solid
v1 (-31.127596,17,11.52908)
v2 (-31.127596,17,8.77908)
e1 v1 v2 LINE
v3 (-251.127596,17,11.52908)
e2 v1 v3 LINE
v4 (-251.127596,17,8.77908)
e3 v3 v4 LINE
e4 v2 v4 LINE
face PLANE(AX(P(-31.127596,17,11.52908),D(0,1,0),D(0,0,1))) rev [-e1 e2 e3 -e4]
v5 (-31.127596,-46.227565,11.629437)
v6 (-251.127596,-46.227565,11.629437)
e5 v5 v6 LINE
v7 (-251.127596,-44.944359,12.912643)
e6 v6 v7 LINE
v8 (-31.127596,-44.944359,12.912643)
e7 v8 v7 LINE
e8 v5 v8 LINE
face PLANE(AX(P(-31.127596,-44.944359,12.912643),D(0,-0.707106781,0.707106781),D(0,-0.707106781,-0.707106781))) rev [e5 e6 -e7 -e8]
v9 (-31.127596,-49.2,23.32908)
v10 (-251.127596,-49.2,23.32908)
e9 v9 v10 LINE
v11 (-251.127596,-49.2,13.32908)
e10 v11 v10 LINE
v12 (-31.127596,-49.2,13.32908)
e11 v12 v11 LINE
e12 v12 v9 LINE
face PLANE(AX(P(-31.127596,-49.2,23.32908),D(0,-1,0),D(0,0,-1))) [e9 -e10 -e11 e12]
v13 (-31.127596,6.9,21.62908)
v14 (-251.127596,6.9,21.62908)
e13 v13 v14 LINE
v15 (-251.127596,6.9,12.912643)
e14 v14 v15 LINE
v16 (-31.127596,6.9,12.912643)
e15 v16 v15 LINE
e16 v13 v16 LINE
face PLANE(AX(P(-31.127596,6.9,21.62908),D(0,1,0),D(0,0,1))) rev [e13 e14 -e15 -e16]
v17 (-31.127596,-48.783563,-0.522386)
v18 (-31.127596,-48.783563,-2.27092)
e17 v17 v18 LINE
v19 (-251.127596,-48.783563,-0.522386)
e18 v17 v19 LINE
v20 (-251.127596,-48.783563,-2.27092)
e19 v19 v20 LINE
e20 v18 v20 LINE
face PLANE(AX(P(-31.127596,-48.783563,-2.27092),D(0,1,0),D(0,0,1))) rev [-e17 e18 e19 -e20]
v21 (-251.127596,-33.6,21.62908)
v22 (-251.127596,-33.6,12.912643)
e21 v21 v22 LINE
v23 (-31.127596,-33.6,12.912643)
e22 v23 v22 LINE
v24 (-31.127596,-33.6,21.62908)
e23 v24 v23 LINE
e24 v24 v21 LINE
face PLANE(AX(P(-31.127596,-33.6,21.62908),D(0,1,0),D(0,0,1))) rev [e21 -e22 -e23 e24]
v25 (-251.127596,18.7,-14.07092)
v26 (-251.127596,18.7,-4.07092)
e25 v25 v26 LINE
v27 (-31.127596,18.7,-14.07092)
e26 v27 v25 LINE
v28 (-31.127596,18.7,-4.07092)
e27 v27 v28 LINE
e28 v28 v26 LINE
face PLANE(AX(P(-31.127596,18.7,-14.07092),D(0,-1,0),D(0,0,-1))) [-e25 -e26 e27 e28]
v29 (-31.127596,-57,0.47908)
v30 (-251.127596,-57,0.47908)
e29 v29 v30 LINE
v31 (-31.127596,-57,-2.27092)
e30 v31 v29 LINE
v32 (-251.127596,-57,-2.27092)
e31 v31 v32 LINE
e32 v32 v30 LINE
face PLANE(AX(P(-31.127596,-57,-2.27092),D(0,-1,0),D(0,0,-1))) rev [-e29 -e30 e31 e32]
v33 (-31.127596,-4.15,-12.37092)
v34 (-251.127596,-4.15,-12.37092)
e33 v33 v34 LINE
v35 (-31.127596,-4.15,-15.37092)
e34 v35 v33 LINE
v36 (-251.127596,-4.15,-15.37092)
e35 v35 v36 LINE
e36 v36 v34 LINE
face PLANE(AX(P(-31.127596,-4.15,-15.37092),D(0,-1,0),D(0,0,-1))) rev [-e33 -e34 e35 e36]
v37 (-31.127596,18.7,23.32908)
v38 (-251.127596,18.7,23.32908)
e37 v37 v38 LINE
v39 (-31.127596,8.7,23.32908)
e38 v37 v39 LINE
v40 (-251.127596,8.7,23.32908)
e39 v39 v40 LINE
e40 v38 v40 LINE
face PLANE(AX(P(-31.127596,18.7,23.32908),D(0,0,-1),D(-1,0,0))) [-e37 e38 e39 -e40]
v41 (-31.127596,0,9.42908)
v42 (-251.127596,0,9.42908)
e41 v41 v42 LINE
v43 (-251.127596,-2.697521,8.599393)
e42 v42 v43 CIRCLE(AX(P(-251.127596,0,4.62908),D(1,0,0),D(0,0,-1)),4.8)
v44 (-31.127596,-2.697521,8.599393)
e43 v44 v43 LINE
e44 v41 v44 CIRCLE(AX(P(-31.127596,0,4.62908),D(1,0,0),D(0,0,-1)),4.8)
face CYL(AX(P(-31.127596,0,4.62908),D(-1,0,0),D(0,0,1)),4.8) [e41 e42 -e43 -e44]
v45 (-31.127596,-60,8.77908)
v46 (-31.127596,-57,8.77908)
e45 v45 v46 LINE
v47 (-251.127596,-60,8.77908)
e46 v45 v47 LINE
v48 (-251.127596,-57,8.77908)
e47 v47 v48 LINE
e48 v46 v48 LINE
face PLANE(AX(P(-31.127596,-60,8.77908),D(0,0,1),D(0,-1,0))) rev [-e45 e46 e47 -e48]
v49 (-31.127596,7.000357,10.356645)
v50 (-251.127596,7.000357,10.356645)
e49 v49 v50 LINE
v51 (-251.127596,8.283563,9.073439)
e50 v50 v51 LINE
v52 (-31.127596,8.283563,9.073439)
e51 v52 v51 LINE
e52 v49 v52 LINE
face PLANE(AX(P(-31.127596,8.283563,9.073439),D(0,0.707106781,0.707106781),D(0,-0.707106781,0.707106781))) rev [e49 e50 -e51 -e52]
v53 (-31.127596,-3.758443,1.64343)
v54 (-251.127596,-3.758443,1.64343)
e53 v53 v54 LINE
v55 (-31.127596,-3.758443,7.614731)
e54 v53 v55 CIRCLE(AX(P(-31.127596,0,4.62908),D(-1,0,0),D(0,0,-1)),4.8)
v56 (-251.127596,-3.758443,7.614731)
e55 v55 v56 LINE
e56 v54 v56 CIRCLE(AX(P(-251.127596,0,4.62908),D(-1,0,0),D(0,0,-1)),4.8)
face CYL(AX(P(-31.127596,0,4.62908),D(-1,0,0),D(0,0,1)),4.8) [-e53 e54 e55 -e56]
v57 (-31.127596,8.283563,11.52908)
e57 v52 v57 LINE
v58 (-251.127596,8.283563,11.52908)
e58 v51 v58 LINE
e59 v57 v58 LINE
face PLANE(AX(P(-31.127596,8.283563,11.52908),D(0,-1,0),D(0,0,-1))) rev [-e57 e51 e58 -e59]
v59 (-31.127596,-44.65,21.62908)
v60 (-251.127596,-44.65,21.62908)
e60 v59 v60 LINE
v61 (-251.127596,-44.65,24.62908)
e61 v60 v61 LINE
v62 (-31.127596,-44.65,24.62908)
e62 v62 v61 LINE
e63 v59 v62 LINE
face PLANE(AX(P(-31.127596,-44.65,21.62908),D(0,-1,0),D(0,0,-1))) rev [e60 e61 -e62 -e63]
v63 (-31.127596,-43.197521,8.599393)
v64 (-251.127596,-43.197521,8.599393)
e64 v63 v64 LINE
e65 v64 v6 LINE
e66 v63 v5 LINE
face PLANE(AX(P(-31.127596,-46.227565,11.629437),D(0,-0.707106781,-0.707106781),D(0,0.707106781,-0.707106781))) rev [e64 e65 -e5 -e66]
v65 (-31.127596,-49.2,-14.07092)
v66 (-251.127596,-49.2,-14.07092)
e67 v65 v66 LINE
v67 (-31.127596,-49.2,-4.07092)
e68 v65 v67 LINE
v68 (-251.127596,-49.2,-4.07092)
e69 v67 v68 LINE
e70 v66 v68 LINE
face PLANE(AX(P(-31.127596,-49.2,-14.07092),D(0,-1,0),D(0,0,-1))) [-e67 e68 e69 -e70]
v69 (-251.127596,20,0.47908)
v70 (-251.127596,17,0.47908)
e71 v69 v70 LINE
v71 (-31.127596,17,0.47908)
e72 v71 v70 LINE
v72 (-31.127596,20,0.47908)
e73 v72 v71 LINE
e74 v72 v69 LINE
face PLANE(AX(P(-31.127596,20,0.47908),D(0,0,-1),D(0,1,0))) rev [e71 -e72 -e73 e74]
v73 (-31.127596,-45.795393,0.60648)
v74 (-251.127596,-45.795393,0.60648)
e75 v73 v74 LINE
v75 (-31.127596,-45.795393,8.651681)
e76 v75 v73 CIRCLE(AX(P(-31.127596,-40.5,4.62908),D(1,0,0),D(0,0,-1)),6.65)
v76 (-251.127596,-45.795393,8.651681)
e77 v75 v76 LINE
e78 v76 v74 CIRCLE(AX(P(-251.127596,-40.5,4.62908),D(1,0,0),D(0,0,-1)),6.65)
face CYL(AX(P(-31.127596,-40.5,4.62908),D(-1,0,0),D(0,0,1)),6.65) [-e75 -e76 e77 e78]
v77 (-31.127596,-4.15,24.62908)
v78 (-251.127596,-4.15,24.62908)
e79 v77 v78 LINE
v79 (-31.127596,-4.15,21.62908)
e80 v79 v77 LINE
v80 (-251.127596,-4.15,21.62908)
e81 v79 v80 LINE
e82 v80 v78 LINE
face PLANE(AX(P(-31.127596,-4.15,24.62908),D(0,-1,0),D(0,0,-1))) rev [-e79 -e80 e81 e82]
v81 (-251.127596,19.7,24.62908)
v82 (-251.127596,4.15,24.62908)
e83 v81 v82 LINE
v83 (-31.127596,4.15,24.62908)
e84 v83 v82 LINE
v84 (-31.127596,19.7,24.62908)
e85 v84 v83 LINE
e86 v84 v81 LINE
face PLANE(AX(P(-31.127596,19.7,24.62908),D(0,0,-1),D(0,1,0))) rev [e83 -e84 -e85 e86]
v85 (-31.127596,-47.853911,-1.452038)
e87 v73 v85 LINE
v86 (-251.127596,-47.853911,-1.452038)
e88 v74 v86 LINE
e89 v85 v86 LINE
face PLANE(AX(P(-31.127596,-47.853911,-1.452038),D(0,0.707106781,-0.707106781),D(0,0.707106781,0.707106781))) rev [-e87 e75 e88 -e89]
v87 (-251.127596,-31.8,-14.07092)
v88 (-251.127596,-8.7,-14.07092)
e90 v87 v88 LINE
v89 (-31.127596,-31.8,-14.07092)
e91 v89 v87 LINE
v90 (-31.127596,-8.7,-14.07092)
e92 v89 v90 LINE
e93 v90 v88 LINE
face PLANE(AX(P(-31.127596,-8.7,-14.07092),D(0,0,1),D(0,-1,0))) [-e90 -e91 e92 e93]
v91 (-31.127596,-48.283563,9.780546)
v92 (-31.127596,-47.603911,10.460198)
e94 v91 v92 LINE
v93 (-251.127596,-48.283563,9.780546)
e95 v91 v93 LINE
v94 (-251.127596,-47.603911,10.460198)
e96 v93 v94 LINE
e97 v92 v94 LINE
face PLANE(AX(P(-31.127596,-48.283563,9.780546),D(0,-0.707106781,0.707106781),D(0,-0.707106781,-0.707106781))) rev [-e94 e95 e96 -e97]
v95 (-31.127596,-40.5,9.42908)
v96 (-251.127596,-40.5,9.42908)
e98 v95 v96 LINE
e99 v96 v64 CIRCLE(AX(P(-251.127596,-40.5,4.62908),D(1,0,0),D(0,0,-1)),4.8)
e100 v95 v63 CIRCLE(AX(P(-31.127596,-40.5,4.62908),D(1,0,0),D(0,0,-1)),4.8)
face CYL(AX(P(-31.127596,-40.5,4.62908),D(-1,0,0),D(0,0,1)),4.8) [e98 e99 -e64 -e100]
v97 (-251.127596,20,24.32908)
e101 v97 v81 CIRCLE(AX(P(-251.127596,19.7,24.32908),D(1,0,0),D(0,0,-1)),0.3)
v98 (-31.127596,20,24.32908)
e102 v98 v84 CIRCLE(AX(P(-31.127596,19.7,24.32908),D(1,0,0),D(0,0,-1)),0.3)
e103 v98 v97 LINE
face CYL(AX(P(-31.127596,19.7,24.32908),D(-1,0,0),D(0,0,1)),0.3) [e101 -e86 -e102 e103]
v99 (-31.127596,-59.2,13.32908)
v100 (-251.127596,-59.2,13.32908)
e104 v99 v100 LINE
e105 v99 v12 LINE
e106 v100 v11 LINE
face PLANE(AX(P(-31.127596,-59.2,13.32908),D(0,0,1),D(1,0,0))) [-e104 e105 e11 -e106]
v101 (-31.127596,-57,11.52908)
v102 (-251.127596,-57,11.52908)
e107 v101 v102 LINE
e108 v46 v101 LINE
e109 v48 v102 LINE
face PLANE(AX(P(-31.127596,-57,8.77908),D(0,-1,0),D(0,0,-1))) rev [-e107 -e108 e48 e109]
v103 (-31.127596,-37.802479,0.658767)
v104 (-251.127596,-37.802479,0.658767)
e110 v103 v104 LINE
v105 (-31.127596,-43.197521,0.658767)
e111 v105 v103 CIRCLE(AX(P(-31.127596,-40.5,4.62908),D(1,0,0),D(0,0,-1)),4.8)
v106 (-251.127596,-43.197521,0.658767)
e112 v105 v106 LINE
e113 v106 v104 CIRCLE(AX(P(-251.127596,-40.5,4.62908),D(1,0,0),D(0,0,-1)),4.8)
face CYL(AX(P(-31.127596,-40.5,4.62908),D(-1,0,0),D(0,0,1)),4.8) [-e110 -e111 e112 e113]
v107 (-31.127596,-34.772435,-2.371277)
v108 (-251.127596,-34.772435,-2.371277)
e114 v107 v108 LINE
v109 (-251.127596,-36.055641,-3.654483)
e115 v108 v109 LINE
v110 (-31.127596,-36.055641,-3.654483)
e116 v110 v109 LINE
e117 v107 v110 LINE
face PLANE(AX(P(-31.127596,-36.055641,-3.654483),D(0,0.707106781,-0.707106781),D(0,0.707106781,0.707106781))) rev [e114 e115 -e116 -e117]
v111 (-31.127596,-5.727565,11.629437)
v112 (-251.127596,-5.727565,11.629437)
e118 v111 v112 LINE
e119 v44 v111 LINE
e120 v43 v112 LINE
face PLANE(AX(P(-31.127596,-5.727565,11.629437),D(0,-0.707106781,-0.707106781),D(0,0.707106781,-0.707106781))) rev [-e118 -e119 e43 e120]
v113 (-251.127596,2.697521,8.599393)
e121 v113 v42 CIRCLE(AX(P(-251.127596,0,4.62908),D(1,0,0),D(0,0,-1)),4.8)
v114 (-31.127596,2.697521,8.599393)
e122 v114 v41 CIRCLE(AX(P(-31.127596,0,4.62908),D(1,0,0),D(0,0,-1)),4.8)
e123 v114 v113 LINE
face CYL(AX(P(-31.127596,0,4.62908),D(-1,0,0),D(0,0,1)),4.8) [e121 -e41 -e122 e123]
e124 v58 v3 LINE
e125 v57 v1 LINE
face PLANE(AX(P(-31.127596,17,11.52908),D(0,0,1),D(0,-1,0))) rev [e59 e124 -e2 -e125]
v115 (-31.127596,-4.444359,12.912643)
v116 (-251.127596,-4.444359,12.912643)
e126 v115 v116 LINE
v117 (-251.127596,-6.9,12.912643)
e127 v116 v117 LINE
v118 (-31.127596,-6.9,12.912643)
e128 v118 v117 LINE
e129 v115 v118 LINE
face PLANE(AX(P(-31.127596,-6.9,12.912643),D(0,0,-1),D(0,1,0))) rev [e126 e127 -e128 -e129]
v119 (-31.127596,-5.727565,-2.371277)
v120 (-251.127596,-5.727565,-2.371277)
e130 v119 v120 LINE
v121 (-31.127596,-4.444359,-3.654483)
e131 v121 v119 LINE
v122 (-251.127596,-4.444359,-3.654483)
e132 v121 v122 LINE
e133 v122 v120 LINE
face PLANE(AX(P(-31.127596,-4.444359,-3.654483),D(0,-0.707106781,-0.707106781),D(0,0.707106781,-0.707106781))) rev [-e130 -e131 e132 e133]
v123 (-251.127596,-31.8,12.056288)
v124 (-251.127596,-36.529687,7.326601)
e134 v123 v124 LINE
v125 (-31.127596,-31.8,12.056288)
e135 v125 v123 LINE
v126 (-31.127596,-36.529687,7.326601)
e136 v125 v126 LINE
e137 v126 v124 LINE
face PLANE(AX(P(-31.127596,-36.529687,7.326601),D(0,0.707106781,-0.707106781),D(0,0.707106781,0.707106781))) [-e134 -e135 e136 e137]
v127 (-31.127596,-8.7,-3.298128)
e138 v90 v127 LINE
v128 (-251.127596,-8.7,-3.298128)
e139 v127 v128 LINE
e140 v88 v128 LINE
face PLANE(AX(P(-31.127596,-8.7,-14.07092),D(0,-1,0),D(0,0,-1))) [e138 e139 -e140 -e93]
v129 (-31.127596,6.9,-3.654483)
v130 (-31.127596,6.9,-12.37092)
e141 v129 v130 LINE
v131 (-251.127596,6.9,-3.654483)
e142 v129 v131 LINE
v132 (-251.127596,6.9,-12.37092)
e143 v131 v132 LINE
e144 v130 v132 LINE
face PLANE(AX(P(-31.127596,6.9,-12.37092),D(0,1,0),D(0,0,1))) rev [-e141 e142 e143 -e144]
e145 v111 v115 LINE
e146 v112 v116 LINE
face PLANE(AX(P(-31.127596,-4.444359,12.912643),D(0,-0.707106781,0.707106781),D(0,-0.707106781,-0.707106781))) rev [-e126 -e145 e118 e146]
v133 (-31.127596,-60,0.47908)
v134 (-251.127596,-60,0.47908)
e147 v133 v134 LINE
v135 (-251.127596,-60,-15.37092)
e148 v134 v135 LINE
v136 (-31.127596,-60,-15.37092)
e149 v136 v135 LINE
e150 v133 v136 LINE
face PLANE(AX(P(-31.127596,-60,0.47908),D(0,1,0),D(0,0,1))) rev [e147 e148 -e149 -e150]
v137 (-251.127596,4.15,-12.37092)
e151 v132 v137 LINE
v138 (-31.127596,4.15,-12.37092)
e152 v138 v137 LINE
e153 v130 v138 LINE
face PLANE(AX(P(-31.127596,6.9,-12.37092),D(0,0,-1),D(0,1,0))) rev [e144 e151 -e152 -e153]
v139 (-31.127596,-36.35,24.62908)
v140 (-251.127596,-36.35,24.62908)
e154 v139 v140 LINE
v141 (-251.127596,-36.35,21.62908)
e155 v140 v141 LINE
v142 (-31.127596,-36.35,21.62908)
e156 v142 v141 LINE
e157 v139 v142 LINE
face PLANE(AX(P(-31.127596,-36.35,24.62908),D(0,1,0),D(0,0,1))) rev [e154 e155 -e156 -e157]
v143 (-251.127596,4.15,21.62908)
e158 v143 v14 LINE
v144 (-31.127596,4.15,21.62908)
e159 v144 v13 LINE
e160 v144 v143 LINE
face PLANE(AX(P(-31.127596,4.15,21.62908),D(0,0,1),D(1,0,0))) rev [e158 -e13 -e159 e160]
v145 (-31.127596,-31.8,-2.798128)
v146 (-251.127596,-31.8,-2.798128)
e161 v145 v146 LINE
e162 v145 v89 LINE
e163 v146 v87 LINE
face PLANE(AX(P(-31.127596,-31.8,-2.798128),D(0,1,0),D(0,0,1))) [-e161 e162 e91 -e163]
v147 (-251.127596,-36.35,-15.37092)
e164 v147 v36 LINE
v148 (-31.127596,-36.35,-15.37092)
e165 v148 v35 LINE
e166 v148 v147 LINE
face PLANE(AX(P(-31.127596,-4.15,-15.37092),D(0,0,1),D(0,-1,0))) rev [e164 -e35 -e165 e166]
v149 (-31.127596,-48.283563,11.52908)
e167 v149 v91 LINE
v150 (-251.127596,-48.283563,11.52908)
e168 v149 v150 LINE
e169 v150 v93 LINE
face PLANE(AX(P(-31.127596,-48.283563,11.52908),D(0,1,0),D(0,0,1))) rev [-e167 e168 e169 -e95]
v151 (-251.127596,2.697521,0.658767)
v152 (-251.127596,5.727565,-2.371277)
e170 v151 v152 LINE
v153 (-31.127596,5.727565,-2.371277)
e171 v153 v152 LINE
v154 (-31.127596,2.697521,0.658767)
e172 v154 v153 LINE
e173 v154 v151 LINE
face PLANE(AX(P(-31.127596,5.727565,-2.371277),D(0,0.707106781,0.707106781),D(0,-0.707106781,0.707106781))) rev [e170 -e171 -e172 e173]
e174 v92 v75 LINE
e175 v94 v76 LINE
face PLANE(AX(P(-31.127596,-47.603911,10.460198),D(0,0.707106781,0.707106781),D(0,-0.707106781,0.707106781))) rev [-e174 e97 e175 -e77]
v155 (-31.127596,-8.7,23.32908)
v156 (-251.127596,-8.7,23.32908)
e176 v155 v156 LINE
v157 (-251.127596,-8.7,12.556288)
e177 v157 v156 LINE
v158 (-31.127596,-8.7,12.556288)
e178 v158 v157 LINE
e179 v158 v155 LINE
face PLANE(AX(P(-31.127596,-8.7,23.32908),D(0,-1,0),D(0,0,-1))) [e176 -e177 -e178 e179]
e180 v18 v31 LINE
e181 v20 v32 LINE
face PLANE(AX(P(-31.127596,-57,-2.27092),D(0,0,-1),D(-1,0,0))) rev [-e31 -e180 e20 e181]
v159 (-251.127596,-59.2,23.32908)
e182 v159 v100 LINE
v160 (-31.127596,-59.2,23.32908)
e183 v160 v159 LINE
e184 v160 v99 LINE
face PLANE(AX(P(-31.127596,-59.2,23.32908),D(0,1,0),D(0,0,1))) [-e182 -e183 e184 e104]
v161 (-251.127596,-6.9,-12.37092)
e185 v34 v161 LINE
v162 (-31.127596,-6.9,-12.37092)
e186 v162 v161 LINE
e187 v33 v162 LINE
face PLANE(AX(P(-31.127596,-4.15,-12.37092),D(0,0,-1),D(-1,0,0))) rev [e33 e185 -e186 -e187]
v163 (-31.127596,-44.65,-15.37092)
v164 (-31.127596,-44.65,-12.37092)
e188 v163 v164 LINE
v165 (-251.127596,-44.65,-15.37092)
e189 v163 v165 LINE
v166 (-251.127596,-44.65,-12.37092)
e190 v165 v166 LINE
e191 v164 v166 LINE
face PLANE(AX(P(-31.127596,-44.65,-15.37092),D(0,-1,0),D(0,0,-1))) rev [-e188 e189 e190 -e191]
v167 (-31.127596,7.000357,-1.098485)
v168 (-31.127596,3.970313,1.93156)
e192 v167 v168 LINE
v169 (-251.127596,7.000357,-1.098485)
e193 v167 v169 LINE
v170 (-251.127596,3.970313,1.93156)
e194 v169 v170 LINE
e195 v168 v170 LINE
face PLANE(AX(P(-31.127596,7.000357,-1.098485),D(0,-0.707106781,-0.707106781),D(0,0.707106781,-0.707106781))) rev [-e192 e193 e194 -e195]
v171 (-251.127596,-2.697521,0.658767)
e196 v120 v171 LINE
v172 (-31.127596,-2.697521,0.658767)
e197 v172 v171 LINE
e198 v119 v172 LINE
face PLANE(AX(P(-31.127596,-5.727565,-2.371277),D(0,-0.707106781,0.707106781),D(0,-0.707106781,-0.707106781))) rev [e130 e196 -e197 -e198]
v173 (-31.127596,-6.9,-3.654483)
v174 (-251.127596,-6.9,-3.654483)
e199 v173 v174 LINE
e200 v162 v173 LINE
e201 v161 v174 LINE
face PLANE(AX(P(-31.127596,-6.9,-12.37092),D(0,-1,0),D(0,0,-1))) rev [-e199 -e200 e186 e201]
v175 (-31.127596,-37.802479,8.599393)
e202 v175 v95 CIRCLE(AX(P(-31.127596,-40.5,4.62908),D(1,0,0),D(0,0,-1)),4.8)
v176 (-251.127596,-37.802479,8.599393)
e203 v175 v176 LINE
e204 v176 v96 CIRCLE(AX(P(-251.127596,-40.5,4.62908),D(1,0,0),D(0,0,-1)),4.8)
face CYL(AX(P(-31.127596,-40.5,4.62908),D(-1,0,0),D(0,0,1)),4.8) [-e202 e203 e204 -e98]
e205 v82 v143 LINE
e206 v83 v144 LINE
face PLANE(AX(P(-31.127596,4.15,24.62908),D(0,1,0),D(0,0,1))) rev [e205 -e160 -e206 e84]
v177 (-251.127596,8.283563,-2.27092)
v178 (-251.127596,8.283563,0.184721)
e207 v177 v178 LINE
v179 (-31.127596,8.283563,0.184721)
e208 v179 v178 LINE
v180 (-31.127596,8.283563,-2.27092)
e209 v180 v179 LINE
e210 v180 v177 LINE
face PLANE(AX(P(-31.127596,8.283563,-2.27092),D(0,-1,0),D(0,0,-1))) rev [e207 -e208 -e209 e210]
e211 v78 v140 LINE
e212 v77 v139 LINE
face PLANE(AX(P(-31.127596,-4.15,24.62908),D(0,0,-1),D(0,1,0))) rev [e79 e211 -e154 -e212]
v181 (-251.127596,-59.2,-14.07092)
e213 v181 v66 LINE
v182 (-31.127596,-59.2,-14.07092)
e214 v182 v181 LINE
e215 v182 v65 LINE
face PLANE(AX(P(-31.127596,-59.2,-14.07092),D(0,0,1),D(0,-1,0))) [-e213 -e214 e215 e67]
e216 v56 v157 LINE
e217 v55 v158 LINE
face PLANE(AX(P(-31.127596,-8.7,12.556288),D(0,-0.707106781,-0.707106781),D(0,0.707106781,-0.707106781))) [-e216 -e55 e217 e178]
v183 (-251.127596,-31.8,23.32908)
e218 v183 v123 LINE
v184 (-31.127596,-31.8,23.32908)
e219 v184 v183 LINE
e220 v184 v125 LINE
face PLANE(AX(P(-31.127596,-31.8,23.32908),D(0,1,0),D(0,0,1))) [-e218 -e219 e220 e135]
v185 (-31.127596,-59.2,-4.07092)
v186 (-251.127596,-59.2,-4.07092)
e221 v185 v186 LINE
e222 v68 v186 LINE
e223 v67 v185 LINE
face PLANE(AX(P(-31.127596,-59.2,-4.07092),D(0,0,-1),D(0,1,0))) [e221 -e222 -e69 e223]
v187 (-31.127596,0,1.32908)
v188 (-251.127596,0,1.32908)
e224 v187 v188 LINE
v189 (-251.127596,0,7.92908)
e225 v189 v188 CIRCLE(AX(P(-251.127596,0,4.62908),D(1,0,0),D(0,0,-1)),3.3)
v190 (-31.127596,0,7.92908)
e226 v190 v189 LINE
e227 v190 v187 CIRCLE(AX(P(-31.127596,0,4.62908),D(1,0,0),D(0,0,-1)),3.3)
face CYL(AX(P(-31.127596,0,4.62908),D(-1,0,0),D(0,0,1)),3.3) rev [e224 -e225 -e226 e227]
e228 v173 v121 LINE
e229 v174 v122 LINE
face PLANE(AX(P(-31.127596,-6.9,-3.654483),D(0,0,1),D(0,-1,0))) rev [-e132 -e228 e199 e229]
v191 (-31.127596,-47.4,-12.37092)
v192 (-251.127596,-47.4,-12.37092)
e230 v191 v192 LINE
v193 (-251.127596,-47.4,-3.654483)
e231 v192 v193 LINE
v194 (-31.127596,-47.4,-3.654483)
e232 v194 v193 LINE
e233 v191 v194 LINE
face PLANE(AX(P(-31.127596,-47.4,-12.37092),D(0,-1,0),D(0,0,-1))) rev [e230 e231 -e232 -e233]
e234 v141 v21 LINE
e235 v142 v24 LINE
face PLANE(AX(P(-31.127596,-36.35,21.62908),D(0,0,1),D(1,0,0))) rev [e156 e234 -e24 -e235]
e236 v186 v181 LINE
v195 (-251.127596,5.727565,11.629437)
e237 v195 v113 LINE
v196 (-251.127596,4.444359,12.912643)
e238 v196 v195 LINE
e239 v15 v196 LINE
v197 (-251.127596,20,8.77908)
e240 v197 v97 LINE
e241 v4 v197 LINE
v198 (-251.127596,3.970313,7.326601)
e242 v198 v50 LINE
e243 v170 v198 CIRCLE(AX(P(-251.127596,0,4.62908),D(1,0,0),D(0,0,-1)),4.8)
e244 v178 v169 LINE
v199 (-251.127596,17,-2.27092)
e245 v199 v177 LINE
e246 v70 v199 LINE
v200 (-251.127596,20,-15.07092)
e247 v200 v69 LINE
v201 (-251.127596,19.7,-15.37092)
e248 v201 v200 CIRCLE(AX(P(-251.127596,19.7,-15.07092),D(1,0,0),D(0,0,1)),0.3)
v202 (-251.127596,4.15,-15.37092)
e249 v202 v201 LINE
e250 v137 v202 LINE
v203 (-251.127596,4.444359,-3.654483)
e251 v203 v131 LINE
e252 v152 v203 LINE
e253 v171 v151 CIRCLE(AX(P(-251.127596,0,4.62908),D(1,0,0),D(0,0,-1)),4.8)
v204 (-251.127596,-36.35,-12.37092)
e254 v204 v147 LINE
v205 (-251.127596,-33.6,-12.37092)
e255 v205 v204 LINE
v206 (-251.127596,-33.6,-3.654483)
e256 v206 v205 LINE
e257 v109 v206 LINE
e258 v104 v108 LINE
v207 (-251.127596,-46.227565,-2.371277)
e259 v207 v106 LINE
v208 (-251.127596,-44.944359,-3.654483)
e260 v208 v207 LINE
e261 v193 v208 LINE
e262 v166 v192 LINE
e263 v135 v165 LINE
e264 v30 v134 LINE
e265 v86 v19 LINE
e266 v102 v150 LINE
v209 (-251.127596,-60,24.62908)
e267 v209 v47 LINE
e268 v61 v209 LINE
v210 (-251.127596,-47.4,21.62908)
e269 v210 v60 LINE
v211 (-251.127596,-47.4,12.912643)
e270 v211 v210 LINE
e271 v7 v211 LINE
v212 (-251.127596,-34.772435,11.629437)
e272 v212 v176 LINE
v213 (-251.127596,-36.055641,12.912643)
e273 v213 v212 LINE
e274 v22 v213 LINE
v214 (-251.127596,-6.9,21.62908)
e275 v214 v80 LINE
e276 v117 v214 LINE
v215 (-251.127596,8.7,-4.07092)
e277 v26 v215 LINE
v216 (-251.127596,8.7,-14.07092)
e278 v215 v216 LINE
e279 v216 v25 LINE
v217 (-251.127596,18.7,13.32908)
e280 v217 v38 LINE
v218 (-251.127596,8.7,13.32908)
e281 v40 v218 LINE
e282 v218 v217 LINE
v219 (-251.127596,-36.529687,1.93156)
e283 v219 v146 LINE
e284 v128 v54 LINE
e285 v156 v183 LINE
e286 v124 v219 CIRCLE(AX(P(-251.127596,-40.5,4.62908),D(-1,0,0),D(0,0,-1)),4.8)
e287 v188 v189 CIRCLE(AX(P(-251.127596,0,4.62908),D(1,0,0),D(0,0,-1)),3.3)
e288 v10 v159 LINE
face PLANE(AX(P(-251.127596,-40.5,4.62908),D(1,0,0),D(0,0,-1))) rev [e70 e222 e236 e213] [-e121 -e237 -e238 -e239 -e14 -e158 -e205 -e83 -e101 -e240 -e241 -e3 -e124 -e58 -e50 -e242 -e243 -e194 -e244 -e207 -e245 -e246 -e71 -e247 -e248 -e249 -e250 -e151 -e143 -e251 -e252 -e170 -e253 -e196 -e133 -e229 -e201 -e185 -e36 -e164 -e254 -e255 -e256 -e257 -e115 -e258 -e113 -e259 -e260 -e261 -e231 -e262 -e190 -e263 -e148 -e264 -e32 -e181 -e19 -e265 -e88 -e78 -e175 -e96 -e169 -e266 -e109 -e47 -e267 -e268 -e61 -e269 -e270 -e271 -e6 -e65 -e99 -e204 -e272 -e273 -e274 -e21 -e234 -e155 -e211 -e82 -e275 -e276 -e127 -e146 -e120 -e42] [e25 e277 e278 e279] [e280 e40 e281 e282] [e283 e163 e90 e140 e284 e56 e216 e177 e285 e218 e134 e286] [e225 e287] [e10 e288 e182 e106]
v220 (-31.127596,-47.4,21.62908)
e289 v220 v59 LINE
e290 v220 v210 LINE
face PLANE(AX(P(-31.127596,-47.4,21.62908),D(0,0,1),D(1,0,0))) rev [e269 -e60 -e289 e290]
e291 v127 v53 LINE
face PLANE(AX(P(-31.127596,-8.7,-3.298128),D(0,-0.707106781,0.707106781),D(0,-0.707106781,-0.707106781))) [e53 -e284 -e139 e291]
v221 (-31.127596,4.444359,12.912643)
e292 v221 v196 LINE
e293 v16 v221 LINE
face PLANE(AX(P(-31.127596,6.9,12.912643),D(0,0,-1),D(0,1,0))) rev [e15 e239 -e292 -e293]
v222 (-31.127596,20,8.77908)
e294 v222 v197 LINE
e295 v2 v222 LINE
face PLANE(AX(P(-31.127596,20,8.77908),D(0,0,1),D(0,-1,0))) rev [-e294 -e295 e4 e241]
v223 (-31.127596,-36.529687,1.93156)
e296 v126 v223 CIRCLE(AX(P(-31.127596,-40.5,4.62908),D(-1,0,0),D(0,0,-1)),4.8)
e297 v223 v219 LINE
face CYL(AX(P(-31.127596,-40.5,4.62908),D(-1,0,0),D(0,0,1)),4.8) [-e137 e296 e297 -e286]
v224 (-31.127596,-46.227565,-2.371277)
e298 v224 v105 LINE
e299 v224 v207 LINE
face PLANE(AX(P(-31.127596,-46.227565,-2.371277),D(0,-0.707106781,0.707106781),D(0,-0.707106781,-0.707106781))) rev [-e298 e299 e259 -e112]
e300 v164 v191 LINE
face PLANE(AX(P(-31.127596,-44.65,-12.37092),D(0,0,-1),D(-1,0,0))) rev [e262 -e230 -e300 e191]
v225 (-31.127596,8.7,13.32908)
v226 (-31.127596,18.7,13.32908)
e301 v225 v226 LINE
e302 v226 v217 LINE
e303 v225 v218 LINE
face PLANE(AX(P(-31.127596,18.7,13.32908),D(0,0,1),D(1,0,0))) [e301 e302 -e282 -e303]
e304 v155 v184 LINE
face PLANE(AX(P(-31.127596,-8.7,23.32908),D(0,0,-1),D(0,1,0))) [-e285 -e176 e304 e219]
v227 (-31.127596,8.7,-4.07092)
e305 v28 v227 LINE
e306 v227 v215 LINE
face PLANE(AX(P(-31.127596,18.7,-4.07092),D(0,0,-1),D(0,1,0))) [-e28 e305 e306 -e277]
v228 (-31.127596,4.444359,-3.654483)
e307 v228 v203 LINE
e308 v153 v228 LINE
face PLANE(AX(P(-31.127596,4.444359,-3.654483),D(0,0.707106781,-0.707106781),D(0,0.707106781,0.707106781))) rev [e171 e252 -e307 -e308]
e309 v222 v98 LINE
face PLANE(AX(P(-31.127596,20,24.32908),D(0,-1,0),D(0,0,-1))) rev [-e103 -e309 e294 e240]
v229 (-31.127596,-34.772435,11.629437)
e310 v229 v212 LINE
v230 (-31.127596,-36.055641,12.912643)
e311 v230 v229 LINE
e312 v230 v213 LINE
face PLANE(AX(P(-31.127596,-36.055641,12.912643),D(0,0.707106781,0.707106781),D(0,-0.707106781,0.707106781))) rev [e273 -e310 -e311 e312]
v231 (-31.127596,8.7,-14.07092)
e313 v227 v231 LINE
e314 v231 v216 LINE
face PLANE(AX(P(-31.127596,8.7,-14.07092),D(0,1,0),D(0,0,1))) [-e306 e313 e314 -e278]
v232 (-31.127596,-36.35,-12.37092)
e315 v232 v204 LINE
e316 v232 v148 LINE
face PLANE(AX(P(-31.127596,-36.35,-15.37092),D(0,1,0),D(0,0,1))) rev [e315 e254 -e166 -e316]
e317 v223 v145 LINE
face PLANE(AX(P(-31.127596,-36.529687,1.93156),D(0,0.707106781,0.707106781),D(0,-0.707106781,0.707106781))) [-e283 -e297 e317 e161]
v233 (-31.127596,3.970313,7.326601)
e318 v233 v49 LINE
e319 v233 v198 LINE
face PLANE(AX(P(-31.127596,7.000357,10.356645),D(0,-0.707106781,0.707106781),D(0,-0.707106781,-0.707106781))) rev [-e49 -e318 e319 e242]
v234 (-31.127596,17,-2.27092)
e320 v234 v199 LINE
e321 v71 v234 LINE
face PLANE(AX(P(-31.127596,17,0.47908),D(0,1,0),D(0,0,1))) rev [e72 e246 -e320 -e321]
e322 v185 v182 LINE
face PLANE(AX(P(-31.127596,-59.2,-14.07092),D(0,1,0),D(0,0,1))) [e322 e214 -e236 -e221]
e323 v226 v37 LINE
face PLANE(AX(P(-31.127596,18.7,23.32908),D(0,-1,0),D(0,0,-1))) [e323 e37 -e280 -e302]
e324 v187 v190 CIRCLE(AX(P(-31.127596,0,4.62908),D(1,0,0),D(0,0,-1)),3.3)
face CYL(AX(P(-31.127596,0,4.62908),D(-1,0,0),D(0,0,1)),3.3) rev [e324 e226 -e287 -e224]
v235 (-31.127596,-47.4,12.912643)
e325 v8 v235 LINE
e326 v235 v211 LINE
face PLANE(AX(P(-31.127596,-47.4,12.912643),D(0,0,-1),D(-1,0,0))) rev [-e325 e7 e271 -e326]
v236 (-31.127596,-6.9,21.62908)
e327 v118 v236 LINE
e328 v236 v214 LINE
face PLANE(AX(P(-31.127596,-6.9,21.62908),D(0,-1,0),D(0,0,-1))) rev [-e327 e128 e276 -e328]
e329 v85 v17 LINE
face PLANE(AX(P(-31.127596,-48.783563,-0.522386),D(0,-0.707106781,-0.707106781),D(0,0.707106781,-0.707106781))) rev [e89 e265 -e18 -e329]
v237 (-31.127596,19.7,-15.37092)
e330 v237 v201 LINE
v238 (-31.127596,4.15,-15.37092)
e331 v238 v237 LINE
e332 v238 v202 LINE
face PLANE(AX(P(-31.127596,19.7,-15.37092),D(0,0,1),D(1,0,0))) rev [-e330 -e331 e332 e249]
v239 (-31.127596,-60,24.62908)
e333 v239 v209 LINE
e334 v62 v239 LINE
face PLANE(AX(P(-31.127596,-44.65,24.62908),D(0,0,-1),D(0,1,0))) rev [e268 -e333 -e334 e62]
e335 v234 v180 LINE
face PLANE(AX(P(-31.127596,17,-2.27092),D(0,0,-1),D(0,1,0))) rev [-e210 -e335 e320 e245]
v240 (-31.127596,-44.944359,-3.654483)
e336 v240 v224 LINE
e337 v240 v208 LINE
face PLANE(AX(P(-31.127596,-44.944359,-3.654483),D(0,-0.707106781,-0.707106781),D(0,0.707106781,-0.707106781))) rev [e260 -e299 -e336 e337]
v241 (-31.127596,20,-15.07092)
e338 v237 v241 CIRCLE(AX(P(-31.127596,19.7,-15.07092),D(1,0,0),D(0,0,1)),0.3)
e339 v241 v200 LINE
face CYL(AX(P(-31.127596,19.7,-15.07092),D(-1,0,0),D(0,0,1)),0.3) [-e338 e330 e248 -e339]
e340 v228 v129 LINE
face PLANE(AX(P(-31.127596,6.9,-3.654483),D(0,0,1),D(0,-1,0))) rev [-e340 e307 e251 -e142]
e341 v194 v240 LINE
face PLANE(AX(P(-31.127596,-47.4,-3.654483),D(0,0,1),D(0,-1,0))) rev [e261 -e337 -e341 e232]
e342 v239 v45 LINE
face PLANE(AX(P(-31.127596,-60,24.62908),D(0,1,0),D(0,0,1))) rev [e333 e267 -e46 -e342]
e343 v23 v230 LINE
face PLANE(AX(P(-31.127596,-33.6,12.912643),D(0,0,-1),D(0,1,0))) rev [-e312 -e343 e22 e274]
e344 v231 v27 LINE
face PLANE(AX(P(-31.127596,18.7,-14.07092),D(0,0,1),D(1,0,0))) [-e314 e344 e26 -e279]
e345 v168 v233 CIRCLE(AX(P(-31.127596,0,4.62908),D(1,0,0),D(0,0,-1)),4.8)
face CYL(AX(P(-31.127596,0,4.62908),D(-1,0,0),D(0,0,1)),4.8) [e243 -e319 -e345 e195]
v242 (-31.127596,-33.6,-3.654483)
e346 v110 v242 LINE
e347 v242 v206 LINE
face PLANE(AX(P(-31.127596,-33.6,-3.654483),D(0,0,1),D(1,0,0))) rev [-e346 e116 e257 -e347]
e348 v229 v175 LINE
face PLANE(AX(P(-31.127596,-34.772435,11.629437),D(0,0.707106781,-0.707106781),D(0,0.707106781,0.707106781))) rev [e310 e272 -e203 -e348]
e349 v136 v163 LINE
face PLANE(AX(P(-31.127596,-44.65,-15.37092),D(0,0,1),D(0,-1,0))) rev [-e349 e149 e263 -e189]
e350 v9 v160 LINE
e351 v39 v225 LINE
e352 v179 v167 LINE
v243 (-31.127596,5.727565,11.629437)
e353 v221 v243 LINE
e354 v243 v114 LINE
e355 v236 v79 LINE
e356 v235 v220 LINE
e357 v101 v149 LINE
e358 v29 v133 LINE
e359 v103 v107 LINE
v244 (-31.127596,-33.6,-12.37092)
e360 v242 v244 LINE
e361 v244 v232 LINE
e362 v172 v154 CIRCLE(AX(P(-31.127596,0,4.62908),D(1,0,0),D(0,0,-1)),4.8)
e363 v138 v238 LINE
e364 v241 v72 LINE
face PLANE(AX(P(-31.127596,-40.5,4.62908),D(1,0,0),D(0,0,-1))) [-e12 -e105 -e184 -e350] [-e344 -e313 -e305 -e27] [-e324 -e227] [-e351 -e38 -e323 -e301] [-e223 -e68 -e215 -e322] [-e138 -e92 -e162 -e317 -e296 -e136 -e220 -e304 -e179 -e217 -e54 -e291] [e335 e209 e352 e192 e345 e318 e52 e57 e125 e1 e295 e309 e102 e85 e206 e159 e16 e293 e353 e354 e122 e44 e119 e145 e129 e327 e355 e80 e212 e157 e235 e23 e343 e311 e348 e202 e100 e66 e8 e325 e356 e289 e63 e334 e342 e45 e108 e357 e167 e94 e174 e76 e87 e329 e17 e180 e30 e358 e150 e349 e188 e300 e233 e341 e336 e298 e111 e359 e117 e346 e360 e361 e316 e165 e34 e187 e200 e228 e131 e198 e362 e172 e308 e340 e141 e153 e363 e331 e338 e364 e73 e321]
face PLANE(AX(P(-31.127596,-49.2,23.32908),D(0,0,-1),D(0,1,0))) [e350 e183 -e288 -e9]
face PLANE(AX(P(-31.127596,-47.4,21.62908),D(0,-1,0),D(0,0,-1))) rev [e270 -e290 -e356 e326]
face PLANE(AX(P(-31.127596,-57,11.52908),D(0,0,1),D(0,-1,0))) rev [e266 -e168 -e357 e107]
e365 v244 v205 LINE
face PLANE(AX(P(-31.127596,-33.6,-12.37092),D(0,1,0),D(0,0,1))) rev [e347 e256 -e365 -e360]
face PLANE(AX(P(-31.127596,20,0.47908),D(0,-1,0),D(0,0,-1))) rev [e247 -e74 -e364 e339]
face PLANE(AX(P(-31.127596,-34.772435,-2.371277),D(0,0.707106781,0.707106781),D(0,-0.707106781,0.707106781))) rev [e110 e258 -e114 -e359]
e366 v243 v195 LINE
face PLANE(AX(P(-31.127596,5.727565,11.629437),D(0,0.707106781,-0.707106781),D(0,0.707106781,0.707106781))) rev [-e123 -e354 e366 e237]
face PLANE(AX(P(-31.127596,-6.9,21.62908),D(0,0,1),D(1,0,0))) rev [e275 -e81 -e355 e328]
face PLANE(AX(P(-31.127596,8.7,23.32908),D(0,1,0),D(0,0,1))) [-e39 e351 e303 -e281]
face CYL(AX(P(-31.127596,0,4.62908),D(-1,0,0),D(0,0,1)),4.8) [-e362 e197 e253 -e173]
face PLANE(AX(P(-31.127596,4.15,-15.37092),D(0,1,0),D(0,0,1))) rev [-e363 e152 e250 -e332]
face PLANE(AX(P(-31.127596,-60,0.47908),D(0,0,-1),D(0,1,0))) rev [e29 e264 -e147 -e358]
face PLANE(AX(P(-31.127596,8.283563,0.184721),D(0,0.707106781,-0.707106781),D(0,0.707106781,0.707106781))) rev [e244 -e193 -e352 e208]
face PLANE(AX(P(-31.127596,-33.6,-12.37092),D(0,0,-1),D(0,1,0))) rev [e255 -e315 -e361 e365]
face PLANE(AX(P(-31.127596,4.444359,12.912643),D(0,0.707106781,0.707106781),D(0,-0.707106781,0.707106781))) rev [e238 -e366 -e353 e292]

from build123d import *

# Parameters (mm, degrees)
SKETCH13_R                               = 3.3
SKETCH13_W                               = 10
SKETCH13_H                               = 10
ALUMINUM_PROFILE_40_X_80L_X_R0_3_1_DEPTH = 220


with BuildPart() as part:
    # Sketch13 → Aluminum profile 40 X 80L X R0.3(1) (new body)
    with BuildSketch(Plane(origin=(-251.127596439, 0, 4.629080119), x_dir=(0, 0, -1), z_dir=(1, 0, 0))):
        with BuildLine():
            Line((-19.7, 20), (-4.15, 20))
            Line((-4.15, 20), (-4.15, 17))
            Line((-4.15, 17), (-6.9, 17))
            Line((-6.9, 17), (-6.9, 8.28356292))
            Line((-6.9, 8.28356292), (-4.444359142, 8.28356292))
            Line((-4.444359142, 8.28356292), (-5.727564928, 7.000357134))
            Line((-5.727564928, 7.000357134), (-2.697520513, 3.970312719))
            ThreePointArc((-2.697520513, 3.970312719), (0, 4.8), (2.697520513, 3.970312719))
            Line((2.697520513, 3.970312719), (5.727564928, 7.000357134))
            Line((5.727564928, 7.000357134), (4.444359142, 8.28356292))
            Line((4.444359142, 8.28356292), (6.9, 8.28356292))
            Line((6.9, 8.28356292), (6.9, 17))
            Line((6.9, 17), (4.15, 17))
            Line((4.15, 17), (4.15, 20))
            Line((4.15, 20), (19.7, 20))
            ThreePointArc((19.7, 20), (19.912132034, 19.912132034), (20, 19.7))
            Line((20, 19.7), (20, 4.15))
            Line((20, 4.15), (17, 4.15))
            Line((17, 4.15), (17, 6.9))
            Line((17, 6.9), (8.28356292, 6.9))
            Line((8.28356292, 6.9), (8.28356292, 4.444359142))
            Line((8.28356292, 4.444359142), (7.000357134, 5.727564928))
            Line((7.000357134, 5.727564928), (3.970312719, 2.697520513))
            ThreePointArc((3.970312719, 2.697520513), (4.8, 0), (3.970312719, -2.697520513))
            Line((3.970312719, -2.697520513), (7.000357134, -5.727564928))
            Line((7.000357134, -5.727564928), (8.28356292, -4.444359142))
            Line((8.28356292, -4.444359142), (8.28356292, -6.9))
            Line((8.28356292, -6.9), (17, -6.9))
            Line((17, -6.9), (17, -4.15))
            Line((17, -4.15), (20, -4.15))
            Line((20, -4.15), (20, -36.35))
            Line((20, -36.35), (17, -36.35))
            Line((17, -36.35), (17, -33.6))
            Line((17, -33.6), (8.28356292, -33.6))
            Line((8.28356292, -33.6), (8.28356292, -36.055640858))
            Line((8.28356292, -36.055640858), (7.000357134, -34.772435072))
            Line((7.000357134, -34.772435072), (3.970312719, -37.802479487))
            ThreePointArc((3.970312719, -37.802479487), (4.8, -40.5), (3.970312719, -43.197520513))
            Line((3.970312719, -43.197520513), (7.000357134, -46.227564928))
            Line((7.000357134, -46.227564928), (8.28356292, -44.944359142))
            Line((8.28356292, -44.944359142), (8.28356292, -47.4))
            Line((8.28356292, -47.4), (17, -47.4))
            Line((17, -47.4), (17, -44.65))
            Line((17, -44.65), (20, -44.65))
            Line((20, -44.65), (20, -60))
            Line((20, -60), (4.15, -60))
            Line((4.15, -60), (4.15, -57))
            Line((4.15, -57), (6.9, -57))
            Line((6.9, -57), (6.9, -48.78356292))
            Line((6.9, -48.78356292), (5.151465923, -48.78356292))
            Line((5.151465923, -48.78356292), (6.081118318, -47.853910524))
            Line((6.081118318, -47.853910524), (4.02260057, -45.795392776))
            ThreePointArc((4.02260057, -45.795392776), (0, -47.15), (-4.02260057, -45.795392776))
            Line((-4.02260057, -45.795392776), (-5.831118318, -47.603910524))
            Line((-5.831118318, -47.603910524), (-5.151465923, -48.28356292))
            Line((-5.151465923, -48.28356292), (-6.9, -48.28356292))
            Line((-6.9, -48.28356292), (-6.9, -57))
            Line((-6.9, -57), (-4.15, -57))
            Line((-4.15, -57), (-4.15, -60))
            Line((-4.15, -60), (-20, -60))
            Line((-20, -60), (-20, -44.65))
            Line((-20, -44.65), (-17, -44.65))
            Line((-17, -44.65), (-17, -47.4))
            Line((-17, -47.4), (-8.28356292, -47.4))
            Line((-8.28356292, -47.4), (-8.28356292, -44.944359142))
            Line((-8.28356292, -44.944359142), (-7.000357134, -46.227564928))
            Line((-7.000357134, -46.227564928), (-3.970312719, -43.197520513))
            ThreePointArc((-3.970312719, -43.197520513), (-4.8, -40.5), (-3.970312719, -37.802479487))
            Line((-3.970312719, -37.802479487), (-7.000357134, -34.772435072))
            Line((-7.000357134, -34.772435072), (-8.28356292, -36.055640858))
            Line((-8.28356292, -36.055640858), (-8.28356292, -33.6))
            Line((-8.28356292, -33.6), (-17, -33.6))
            Line((-17, -33.6), (-17, -36.35))
            Line((-17, -36.35), (-20, -36.35))
            Line((-20, -36.35), (-20, -4.15))
            Line((-20, -4.15), (-17, -4.15))
            Line((-17, -4.15), (-17, -6.9))
            Line((-17, -6.9), (-8.28356292, -6.9))
            Line((-8.28356292, -6.9), (-8.28356292, -4.444359142))
            Line((-8.28356292, -4.444359142), (-7.000357134, -5.727564928))
            Line((-7.000357134, -5.727564928), (-3.970312719, -2.697520513))
            ThreePointArc((-3.970312719, -2.697520513), (-4.8, 0), (-3.970312719, 2.697520513))
            Line((-3.970312719, 2.697520513), (-7.000357134, 5.727564928))
            Line((-7.000357134, 5.727564928), (-8.28356292, 4.444359142))
            Line((-8.28356292, 4.444359142), (-8.28356292, 6.9))
            Line((-8.28356292, 6.9), (-17, 6.9))
            Line((-17, 6.9), (-17, 4.15))
            Line((-17, 4.15), (-20, 4.15))
            Line((-20, 4.15), (-20, 19.7))
            ThreePointArc((-20, 19.7), (-19.912132034, 19.912132034), (-19.7, 20))
        make_face()
        Circle(SKETCH13_R, mode=Mode.SUBTRACT)
        with BuildLine():
            Line((-18.7, -8.7), (-18.7, -31.8))
            Line((-18.7, -31.8), (-7.427207794, -31.8))
            Line((-7.427207794, -31.8), (-2.697520513, -36.529687281))
            ThreePointArc((-2.697520513, -36.529687281), (0, -35.7), (2.697520513, -36.529687281))
            Line((2.697520513, -36.529687281), (7.427207794, -31.8))
            Line((7.427207794, -31.8), (18.7, -31.8))
            Line((18.7, -31.8), (18.7, -8.7))
            Line((18.7, -8.7), (7.927207794, -8.7))
            Line((7.927207794, -8.7), (2.985650464, -3.75844267))
            ThreePointArc((2.985650464, -3.75844267), (0, -4.8), (-2.985650464, -3.75844267))
            Line((-2.985650464, -3.75844267), (-7.927207794, -8.7))
            Line((-7.927207794, -8.7), (-18.7, -8.7))
        make_face(mode=Mode.SUBTRACT)
        with Locations((-13.7, 13.7)):
            Rectangle(SKETCH13_W, SKETCH13_H, mode=Mode.SUBTRACT)
        with Locations((13.7, 13.7)):
            Rectangle(SKETCH13_W, SKETCH13_H, mode=Mode.SUBTRACT)
        with Locations((-13.7, -54.2)):
            Rectangle(SKETCH13_W, SKETCH13_H, mode=Mode.SUBTRACT)
        with Locations((13.7, -54.2)):
            Rectangle(SKETCH13_W, SKETCH13_H, mode=Mode.SUBTRACT)
    extrude(amount=ALUMINUM_PROFILE_40_X_80L_X_R0_3_1_DEPTH)


solid = part.part
